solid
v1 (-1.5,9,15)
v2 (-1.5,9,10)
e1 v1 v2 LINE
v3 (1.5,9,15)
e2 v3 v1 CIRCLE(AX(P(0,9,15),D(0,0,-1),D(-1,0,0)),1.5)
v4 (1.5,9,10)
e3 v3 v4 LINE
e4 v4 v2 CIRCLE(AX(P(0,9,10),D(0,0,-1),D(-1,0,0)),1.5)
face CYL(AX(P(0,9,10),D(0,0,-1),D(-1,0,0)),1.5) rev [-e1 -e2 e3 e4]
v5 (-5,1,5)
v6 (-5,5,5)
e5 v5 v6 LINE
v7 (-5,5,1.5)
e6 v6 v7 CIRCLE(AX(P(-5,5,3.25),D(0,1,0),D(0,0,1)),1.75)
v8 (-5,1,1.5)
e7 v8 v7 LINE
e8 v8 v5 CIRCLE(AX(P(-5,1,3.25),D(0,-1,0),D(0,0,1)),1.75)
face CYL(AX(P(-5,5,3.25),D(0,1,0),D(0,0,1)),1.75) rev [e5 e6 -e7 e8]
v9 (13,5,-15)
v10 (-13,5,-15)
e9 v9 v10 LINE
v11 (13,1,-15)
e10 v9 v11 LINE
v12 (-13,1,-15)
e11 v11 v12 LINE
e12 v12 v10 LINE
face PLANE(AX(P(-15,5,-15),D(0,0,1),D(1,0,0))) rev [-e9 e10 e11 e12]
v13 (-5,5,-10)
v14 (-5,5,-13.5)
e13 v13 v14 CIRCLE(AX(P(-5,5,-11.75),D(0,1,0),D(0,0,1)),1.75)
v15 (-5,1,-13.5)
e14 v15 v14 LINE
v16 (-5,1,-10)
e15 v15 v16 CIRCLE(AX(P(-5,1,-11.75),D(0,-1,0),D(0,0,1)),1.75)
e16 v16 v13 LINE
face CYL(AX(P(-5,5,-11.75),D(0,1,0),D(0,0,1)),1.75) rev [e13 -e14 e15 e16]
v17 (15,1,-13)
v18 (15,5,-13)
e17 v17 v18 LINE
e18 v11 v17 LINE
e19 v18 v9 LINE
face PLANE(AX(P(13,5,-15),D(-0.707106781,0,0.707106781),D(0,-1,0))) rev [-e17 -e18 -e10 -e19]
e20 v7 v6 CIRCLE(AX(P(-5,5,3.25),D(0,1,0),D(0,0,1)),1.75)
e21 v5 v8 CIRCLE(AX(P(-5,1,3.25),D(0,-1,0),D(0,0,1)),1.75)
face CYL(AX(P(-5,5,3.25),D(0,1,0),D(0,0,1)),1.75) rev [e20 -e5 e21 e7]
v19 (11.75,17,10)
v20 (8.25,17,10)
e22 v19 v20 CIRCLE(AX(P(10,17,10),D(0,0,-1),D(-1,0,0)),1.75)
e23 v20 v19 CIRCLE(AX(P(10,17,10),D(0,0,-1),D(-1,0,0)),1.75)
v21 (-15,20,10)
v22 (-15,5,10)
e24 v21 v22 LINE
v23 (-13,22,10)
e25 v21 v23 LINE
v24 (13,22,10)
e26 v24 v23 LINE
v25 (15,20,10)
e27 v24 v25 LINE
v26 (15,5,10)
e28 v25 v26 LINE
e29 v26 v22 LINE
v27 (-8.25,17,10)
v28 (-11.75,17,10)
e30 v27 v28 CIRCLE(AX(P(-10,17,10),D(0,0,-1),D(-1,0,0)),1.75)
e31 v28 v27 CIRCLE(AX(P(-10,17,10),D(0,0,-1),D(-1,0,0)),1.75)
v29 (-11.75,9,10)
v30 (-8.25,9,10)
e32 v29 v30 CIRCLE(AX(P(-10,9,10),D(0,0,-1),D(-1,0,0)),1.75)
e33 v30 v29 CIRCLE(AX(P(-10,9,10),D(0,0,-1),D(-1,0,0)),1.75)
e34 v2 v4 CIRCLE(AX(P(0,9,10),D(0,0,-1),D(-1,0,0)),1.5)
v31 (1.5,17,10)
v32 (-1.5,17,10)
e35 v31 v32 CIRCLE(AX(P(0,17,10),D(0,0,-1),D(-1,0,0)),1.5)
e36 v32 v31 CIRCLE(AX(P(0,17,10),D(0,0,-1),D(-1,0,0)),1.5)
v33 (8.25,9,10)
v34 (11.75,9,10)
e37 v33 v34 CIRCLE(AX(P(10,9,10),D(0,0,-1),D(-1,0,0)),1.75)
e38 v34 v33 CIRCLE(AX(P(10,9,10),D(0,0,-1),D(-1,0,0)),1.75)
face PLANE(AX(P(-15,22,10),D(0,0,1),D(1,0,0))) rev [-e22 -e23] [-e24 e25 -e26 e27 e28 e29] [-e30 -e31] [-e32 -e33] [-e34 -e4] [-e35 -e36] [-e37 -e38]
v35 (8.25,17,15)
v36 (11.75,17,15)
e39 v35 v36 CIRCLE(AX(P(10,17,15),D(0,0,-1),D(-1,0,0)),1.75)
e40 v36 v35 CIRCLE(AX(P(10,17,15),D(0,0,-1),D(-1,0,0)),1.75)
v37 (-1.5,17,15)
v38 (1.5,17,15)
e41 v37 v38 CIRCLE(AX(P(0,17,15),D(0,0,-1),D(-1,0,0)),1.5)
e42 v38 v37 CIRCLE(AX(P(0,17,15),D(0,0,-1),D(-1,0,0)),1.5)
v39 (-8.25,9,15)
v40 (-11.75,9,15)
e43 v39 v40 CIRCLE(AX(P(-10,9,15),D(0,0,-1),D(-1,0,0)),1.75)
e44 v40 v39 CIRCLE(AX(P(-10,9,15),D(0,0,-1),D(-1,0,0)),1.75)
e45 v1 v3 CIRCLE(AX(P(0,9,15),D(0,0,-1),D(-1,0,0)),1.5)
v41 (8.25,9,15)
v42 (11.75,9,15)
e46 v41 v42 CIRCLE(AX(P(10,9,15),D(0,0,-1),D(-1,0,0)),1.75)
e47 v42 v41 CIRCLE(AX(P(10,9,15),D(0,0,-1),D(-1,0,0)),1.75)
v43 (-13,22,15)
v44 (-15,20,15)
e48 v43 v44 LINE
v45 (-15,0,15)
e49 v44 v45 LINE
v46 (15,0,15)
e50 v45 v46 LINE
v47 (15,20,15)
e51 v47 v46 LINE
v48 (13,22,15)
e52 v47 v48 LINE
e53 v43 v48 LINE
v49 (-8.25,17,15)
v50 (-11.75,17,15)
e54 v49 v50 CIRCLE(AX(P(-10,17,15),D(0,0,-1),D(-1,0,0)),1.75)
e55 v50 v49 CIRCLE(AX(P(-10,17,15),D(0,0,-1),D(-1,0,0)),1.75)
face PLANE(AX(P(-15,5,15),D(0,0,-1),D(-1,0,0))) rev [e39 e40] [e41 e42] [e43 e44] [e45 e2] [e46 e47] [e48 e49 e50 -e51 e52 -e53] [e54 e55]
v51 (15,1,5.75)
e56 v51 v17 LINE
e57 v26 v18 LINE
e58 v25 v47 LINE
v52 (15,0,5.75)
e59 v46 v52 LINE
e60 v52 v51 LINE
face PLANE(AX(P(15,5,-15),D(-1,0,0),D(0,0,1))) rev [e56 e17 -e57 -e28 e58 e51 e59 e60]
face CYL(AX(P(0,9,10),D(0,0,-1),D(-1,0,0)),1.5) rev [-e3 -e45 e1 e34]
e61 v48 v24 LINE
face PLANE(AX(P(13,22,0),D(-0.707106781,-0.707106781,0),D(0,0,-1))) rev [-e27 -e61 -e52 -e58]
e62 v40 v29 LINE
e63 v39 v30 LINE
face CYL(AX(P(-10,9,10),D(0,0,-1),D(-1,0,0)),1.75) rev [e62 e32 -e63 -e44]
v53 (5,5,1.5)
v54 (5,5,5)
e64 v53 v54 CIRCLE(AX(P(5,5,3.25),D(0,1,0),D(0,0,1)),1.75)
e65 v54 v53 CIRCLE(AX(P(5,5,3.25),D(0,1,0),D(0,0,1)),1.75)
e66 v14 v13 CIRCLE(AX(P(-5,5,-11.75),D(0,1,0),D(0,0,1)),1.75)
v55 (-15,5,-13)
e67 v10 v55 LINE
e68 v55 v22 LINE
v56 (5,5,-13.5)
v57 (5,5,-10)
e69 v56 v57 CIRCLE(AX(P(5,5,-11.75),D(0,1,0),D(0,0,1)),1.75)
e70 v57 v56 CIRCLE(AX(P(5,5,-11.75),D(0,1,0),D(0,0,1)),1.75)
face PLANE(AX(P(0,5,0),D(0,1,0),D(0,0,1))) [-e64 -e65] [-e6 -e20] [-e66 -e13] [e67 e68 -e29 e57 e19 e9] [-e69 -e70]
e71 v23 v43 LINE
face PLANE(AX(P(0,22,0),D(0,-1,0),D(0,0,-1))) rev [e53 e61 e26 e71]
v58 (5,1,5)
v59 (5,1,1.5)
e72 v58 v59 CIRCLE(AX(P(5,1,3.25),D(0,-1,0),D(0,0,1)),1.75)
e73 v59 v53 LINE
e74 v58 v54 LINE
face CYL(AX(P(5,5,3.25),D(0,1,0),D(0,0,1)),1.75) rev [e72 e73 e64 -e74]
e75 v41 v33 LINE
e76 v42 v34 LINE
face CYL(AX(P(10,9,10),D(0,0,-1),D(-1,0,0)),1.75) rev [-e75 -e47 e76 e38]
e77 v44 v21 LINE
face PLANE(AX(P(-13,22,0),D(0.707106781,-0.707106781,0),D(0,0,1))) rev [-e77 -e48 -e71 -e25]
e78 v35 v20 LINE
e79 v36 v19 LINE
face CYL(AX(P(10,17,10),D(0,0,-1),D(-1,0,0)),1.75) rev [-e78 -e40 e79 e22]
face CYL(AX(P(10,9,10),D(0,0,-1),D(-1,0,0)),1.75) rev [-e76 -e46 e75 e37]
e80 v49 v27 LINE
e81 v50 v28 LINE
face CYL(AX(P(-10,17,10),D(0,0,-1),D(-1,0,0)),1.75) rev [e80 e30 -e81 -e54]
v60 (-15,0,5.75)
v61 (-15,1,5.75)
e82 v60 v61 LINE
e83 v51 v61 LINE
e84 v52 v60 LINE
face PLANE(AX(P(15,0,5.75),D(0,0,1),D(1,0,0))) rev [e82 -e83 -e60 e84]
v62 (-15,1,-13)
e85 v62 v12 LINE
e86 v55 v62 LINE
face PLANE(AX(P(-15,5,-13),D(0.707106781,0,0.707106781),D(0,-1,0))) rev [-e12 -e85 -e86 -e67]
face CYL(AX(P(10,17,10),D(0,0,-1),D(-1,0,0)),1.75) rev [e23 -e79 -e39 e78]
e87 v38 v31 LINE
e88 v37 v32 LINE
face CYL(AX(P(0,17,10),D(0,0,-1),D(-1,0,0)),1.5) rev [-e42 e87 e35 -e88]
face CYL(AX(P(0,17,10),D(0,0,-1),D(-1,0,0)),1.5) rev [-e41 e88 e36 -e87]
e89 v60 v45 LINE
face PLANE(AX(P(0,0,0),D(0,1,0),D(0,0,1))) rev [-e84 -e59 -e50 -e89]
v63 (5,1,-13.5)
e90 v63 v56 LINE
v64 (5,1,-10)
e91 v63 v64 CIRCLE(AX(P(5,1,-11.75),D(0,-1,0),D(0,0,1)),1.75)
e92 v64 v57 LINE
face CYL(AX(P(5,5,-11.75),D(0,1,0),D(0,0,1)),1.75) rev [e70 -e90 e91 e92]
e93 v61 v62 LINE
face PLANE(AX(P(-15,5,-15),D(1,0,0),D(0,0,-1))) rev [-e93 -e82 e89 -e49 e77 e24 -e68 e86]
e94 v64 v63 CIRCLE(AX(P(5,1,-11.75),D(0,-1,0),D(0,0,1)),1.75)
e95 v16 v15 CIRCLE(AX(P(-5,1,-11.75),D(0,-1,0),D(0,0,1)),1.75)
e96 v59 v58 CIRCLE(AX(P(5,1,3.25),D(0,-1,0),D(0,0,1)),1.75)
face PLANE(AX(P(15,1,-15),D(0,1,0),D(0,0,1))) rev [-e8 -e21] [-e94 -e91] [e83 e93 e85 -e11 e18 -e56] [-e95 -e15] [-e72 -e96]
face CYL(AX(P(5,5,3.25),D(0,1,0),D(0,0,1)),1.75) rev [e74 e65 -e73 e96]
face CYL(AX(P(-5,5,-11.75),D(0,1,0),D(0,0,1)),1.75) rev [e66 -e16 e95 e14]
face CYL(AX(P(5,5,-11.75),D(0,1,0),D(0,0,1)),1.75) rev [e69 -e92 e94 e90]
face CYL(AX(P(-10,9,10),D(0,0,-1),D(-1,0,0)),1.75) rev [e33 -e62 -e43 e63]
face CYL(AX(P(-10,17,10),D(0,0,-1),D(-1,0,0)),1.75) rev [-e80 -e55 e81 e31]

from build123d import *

# Parameters (mm, degrees)
SKETCH_1_W                  = 30
SKETCH_1_H                  = 30
EXTRUDE_1_DEPTH             = 5
SKETCH_2_W                  = 30
SKETCH_2_H                  = 5
EXTRUDE_2_DEPTH             = 17
HOLE_WIZARD_3_5_3_5_1_D     = 3.5
HOLE_WIZARD_3_5_3_5_1_DEPTH = 12.4
HOLE_WIZARD_3_5_3_5_1_TIP   = 1.051506083
SKETCH_5_W                  = 20.75
SKETCH_5_H                  = 1
CUT_EXTRUDE_1_DEPTH         = 41.11234224
CHAMFER_1_SIZE              = 2
HOLE_WIZARD_3_5_3_5_2_D     = 3.5
HOLE_WIZARD_3_5_3_5_2_DEPTH = 12.4
HOLE_WIZARD_3_5_3_5_2_TIP   = 1.051506083
MM_1_D                      = 3
MM_1_DEPTH                  = 12.4
MM_1_TIP                    = 0.901290929


with BuildPart() as part:
    # 草图1 → 凸台-拉伸1 (new body)
    with BuildSketch(Plane(origin=(0, 0, 0), x_dir=(1, 0, 0), z_dir=(0, 1, 0))):
        Rectangle(SKETCH_1_W, SKETCH_1_H)
    extrude(amount=EXTRUDE_1_DEPTH)

    # 草图2 → 凸台-拉伸2 (add)
    with BuildSketch(Plane(origin=(0, 5, 0), x_dir=(1, 0, 0), z_dir=(0, 1, 0))):
        with Locations((0, -12.5)):
            Rectangle(SKETCH_2_W, SKETCH_2_H)
    extrude(amount=EXTRUDE_2_DEPTH)

    # Ø3.5 (3.5) 直径孔1
    with Locations(Plane(origin=(0, 5, 0), x_dir=(1, 0, 0), z_dir=(0, 1, 0))):
        with Locations((-5, 11.75), (5, 11.75), (5, -3.25), (-5, -3.25)):
            Hole(HOLE_WIZARD_3_5_3_5_1_D / 2, depth=HOLE_WIZARD_3_5_3_5_1_DEPTH)
            with Locations((0, 0, -(HOLE_WIZARD_3_5_3_5_1_DEPTH + HOLE_WIZARD_3_5_3_5_1_TIP / 2))):  # 118° drill point
                Cone(0, HOLE_WIZARD_3_5_3_5_1_D / 2, HOLE_WIZARD_3_5_3_5_1_TIP, mode=Mode.SUBTRACT)

    # 草图5 → 切除-拉伸1 (cut, through all)
    with BuildSketch(Plane.ZY.offset(15)):
        with Locations((-4.625, 0.5)):
            Rectangle(SKETCH_5_W, SKETCH_5_H)
    extrude(amount=-CUT_EXTRUDE_1_DEPTH, mode=Mode.SUBTRACT)

    # 倒角1
    chamfer_1_edges = [part.edges().sort_by_distance(p)[0] for p in [
        (-15, 22, 12.5),
        (15, 22, 12.5),
        (-15, 3, -15),
        (15, 3, -15),
    ]]
    chamfer(chamfer_1_edges, length=CHAMFER_1_SIZE)

    # Ø3.5 (3.5) 直径孔2
    with Locations(Plane(origin=(0, 0, 10), x_dir=(-1, 0, 0), z_dir=(0, 0, -1))):
        with Locations((-10, 17), (10, 17), (-10, 9), (10, 9)):
            Hole(HOLE_WIZARD_3_5_3_5_2_D / 2, depth=HOLE_WIZARD_3_5_3_5_2_DEPTH)
            with Locations((0, 0, -(HOLE_WIZARD_3_5_3_5_2_DEPTH + HOLE_WIZARD_3_5_3_5_2_TIP / 2))):  # 118° drill point
                Cone(0, HOLE_WIZARD_3_5_3_5_2_D / 2, HOLE_WIZARD_3_5_3_5_2_TIP, mode=Mode.SUBTRACT)

    # 大小mm 暗销孔1
    with Locations(Plane(origin=(0, 0, 10), x_dir=(-1, 0, 0), z_dir=(0, 0, -1))):
        with Locations((0, 17), (0, 9)):
            Hole(MM_1_D / 2, depth=MM_1_DEPTH)
            with Locations((0, 0, -(MM_1_DEPTH + MM_1_TIP / 2))):  # 118° drill point
                Cone(0, MM_1_D / 2, MM_1_TIP, mode=Mode.SUBTRACT)


solid = part.part
